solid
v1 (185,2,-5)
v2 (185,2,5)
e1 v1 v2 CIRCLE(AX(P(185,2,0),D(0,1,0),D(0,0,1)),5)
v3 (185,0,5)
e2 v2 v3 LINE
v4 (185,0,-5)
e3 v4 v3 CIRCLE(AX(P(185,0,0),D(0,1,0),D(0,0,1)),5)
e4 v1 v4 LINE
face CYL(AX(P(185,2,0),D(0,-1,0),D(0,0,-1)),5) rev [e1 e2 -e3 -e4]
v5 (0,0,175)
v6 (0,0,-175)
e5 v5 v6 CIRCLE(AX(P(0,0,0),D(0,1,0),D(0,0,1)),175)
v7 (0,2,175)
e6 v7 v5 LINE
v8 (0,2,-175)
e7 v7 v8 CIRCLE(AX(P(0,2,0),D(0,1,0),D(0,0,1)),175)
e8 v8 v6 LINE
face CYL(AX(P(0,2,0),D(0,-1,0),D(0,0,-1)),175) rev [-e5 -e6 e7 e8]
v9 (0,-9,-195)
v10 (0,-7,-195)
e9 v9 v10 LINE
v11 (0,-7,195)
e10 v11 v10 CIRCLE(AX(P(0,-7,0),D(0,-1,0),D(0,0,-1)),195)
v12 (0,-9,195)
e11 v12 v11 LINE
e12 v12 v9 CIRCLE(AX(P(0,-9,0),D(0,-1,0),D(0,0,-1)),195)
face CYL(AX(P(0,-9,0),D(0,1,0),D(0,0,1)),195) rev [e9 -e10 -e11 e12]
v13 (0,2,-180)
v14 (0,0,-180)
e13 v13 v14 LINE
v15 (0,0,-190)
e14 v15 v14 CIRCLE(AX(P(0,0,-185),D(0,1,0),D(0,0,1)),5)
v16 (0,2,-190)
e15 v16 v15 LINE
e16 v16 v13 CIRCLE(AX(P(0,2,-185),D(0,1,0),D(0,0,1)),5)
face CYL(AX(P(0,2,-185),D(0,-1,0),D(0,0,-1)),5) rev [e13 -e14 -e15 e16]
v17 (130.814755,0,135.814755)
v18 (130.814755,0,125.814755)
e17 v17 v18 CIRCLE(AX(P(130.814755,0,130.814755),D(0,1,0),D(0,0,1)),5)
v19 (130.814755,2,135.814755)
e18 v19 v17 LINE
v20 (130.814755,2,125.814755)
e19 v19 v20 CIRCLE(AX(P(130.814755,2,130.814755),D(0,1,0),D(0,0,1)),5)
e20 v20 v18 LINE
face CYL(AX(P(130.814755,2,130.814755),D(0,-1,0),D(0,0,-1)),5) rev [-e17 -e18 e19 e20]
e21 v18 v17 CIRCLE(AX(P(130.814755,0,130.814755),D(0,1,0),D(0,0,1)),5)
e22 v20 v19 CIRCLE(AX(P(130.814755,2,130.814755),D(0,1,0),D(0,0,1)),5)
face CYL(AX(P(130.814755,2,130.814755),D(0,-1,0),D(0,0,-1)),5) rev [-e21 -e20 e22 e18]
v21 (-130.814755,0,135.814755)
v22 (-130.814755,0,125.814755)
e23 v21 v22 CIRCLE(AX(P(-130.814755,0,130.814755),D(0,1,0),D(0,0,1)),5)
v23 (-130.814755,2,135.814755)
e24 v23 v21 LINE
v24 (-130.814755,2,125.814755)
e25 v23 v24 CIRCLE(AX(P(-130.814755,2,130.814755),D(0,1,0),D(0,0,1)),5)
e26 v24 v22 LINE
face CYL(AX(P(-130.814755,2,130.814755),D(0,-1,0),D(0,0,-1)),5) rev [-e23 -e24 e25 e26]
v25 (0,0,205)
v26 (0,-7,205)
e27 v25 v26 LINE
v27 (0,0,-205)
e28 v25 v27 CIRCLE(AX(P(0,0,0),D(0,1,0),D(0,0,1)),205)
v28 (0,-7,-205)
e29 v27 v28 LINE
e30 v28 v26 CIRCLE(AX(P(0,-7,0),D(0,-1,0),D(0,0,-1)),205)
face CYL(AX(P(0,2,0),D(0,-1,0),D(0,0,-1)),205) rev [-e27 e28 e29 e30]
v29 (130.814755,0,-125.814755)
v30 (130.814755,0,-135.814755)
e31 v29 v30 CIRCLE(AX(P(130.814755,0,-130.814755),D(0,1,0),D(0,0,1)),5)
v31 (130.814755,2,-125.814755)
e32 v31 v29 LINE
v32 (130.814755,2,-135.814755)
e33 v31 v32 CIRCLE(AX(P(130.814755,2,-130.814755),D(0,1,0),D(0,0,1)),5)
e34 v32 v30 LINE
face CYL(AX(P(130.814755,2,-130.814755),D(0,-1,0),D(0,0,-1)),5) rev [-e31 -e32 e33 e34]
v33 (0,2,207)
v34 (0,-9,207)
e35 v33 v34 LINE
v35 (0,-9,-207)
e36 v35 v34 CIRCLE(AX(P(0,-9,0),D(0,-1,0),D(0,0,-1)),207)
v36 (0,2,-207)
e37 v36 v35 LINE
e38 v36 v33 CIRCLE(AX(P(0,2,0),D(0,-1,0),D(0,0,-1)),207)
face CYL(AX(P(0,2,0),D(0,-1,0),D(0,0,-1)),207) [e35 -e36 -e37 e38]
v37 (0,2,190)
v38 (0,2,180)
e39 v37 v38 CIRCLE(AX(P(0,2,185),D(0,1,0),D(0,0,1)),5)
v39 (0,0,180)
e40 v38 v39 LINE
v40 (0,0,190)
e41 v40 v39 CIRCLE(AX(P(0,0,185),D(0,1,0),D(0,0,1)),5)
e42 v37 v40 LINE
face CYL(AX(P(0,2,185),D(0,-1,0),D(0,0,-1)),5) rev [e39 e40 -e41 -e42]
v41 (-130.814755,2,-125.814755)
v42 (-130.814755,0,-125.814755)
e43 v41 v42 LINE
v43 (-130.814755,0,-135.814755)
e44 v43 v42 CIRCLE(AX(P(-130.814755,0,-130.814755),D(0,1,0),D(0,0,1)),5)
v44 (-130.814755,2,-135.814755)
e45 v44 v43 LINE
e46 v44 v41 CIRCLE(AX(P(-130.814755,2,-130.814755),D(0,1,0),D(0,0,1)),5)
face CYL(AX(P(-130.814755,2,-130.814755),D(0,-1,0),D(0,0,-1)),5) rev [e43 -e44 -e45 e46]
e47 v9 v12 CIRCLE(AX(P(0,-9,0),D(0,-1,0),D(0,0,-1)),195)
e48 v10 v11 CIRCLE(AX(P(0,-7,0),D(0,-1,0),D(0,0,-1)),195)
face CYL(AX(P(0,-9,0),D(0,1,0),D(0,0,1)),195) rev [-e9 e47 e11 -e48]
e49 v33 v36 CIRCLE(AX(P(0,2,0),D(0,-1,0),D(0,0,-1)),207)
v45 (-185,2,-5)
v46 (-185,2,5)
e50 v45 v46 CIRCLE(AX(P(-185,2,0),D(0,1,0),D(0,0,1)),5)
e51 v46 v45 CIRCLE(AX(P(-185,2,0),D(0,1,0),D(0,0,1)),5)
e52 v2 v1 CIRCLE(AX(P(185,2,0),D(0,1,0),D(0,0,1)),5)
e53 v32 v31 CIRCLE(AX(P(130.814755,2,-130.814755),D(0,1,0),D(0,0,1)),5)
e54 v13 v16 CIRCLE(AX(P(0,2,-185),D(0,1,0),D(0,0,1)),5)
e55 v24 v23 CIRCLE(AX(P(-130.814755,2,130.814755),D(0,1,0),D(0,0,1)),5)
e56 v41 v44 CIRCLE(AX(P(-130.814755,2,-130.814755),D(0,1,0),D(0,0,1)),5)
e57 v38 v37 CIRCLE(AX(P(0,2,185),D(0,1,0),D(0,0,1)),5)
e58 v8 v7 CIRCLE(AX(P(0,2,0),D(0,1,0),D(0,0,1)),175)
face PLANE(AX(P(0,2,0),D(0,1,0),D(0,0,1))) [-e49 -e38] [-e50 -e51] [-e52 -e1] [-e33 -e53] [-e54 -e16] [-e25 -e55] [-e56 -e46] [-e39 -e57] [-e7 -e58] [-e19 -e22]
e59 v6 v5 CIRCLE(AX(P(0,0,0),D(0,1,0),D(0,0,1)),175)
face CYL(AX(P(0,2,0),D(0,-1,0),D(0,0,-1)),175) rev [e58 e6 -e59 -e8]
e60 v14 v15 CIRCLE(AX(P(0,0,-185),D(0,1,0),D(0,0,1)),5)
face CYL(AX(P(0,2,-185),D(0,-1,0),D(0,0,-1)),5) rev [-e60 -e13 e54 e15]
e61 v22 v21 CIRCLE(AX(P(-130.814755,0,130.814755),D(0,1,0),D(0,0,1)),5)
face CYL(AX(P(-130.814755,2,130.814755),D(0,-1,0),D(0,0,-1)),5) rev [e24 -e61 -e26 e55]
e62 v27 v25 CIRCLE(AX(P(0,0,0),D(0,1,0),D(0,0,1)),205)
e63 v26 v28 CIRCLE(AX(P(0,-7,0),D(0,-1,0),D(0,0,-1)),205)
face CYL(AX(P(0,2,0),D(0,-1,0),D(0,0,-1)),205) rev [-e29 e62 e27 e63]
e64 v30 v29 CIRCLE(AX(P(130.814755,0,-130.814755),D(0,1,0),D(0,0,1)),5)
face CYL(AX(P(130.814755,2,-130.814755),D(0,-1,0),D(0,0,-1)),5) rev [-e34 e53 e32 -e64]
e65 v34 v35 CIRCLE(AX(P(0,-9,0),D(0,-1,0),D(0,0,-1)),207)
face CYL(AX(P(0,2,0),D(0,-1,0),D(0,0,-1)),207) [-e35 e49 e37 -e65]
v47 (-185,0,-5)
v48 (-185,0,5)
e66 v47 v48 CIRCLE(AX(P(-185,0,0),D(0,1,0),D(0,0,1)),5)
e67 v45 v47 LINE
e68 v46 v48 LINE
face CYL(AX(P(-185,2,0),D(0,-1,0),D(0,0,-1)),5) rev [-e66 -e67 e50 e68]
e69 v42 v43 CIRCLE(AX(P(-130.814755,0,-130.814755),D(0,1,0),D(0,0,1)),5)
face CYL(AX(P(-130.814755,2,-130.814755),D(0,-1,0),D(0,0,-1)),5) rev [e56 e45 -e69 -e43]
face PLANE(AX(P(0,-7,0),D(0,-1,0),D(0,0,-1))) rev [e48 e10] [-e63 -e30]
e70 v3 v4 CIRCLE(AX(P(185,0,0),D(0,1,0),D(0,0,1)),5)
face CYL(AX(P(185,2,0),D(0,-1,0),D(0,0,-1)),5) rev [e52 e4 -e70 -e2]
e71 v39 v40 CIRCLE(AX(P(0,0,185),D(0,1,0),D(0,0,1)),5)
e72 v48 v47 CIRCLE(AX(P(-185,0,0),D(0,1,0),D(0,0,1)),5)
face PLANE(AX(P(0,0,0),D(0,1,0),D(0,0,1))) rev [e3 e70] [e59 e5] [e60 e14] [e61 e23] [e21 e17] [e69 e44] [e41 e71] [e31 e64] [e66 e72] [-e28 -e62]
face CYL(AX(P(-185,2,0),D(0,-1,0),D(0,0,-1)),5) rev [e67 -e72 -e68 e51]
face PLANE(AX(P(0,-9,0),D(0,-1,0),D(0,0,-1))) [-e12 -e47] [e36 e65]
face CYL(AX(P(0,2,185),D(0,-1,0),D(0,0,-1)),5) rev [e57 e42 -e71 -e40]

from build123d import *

# Parameters (mm, degrees)
SKETCH1_R                = 205
SKETCH1_R_2              = 5
SKETCH1_R_3              = 175
BOSS_EXTRUDE1_DEPTH      = 2
BOSS_EXTRUDE2_DEPTH      = 7
BOSS_EXTRUDE2_DEPTH_BACK = 2
SKETCH2_R                = 207
SKETCH2_R_2              = 205
BOSS_EXTRUDE3_START      = 2
SKETCH3_R                = 207
SKETCH3_R_2              = 195
BOSS_EXTRUDE3_DEPTH      = 2


with BuildPart() as part:
    # Sketch1 → Boss-Extrude1 (new body)
    with BuildSketch(Plane(origin=(0, 0, 0), x_dir=(1, 0, 0), z_dir=(0, 1, 0))):
        with Locations(Location((0, 0, 0), (0, 0, 270))):
            Circle(SKETCH1_R)
        with Locations(Location((-185, 0, 0), (0, 0, 270))):
            Circle(SKETCH1_R_2, mode=Mode.SUBTRACT)
        with Locations(Location((0, 0, 0), (0, 0, 270))):
            Circle(SKETCH1_R_3, mode=Mode.SUBTRACT)
        with Locations(Location((-130.81475452, 130.81475452, 0), (0, 0, 270))):
            Circle(SKETCH1_R_2, mode=Mode.SUBTRACT)
        with Locations(Location((0, 185, 0), (0, 0, 270))):
            Circle(SKETCH1_R_2, mode=Mode.SUBTRACT)
        with Locations(Location((130.81475452, 130.81475452, 0), (0, 0, 270))):
            Circle(SKETCH1_R_2, mode=Mode.SUBTRACT)
        with Locations(Location((185, 0, 0), (0, 0, 270))):
            Circle(SKETCH1_R_2, mode=Mode.SUBTRACT)
        with Locations(Location((130.81475452, -130.81475452, 0), (0, 0, 270))):
            Circle(SKETCH1_R_2, mode=Mode.SUBTRACT)
        with Locations(Location((0, -185, 0), (0, 0, 270))):
            Circle(SKETCH1_R_2, mode=Mode.SUBTRACT)
        with Locations(Location((-130.81475452, -130.81475452, 0), (0, 0, 270))):
            Circle(SKETCH1_R_2, mode=Mode.SUBTRACT)
    extrude(amount=BOSS_EXTRUDE1_DEPTH)

    # Sketch2 → Boss-Extrude2 (add, two sides: drawn at the far end of the back side and taken through both)
    with BuildSketch(Plane.XZ.offset(-BOSS_EXTRUDE2_DEPTH_BACK)):
        with Locations(Location((0, 0, 0), (0, 0, 270))):
            Circle(SKETCH2_R)
        with Locations(Location((0, 0, 0), (0, 0, 270))):
            Circle(SKETCH2_R_2, mode=Mode.SUBTRACT)
    extrude(amount=BOSS_EXTRUDE2_DEPTH + BOSS_EXTRUDE2_DEPTH_BACK)

    # Sketch3 → Boss-Extrude3 (add)
    with BuildSketch(Plane.XZ.offset(7).offset(BOSS_EXTRUDE3_START)):
        with Locations(Location((0, 0, 0), (0, 0, 270))):
            Circle(SKETCH3_R)
        with Locations(Location((0, 0, 0), (0, 0, 270))):
            Circle(SKETCH3_R_2, mode=Mode.SUBTRACT)
    extrude(amount=-BOSS_EXTRUDE3_DEPTH)


solid = part.part
